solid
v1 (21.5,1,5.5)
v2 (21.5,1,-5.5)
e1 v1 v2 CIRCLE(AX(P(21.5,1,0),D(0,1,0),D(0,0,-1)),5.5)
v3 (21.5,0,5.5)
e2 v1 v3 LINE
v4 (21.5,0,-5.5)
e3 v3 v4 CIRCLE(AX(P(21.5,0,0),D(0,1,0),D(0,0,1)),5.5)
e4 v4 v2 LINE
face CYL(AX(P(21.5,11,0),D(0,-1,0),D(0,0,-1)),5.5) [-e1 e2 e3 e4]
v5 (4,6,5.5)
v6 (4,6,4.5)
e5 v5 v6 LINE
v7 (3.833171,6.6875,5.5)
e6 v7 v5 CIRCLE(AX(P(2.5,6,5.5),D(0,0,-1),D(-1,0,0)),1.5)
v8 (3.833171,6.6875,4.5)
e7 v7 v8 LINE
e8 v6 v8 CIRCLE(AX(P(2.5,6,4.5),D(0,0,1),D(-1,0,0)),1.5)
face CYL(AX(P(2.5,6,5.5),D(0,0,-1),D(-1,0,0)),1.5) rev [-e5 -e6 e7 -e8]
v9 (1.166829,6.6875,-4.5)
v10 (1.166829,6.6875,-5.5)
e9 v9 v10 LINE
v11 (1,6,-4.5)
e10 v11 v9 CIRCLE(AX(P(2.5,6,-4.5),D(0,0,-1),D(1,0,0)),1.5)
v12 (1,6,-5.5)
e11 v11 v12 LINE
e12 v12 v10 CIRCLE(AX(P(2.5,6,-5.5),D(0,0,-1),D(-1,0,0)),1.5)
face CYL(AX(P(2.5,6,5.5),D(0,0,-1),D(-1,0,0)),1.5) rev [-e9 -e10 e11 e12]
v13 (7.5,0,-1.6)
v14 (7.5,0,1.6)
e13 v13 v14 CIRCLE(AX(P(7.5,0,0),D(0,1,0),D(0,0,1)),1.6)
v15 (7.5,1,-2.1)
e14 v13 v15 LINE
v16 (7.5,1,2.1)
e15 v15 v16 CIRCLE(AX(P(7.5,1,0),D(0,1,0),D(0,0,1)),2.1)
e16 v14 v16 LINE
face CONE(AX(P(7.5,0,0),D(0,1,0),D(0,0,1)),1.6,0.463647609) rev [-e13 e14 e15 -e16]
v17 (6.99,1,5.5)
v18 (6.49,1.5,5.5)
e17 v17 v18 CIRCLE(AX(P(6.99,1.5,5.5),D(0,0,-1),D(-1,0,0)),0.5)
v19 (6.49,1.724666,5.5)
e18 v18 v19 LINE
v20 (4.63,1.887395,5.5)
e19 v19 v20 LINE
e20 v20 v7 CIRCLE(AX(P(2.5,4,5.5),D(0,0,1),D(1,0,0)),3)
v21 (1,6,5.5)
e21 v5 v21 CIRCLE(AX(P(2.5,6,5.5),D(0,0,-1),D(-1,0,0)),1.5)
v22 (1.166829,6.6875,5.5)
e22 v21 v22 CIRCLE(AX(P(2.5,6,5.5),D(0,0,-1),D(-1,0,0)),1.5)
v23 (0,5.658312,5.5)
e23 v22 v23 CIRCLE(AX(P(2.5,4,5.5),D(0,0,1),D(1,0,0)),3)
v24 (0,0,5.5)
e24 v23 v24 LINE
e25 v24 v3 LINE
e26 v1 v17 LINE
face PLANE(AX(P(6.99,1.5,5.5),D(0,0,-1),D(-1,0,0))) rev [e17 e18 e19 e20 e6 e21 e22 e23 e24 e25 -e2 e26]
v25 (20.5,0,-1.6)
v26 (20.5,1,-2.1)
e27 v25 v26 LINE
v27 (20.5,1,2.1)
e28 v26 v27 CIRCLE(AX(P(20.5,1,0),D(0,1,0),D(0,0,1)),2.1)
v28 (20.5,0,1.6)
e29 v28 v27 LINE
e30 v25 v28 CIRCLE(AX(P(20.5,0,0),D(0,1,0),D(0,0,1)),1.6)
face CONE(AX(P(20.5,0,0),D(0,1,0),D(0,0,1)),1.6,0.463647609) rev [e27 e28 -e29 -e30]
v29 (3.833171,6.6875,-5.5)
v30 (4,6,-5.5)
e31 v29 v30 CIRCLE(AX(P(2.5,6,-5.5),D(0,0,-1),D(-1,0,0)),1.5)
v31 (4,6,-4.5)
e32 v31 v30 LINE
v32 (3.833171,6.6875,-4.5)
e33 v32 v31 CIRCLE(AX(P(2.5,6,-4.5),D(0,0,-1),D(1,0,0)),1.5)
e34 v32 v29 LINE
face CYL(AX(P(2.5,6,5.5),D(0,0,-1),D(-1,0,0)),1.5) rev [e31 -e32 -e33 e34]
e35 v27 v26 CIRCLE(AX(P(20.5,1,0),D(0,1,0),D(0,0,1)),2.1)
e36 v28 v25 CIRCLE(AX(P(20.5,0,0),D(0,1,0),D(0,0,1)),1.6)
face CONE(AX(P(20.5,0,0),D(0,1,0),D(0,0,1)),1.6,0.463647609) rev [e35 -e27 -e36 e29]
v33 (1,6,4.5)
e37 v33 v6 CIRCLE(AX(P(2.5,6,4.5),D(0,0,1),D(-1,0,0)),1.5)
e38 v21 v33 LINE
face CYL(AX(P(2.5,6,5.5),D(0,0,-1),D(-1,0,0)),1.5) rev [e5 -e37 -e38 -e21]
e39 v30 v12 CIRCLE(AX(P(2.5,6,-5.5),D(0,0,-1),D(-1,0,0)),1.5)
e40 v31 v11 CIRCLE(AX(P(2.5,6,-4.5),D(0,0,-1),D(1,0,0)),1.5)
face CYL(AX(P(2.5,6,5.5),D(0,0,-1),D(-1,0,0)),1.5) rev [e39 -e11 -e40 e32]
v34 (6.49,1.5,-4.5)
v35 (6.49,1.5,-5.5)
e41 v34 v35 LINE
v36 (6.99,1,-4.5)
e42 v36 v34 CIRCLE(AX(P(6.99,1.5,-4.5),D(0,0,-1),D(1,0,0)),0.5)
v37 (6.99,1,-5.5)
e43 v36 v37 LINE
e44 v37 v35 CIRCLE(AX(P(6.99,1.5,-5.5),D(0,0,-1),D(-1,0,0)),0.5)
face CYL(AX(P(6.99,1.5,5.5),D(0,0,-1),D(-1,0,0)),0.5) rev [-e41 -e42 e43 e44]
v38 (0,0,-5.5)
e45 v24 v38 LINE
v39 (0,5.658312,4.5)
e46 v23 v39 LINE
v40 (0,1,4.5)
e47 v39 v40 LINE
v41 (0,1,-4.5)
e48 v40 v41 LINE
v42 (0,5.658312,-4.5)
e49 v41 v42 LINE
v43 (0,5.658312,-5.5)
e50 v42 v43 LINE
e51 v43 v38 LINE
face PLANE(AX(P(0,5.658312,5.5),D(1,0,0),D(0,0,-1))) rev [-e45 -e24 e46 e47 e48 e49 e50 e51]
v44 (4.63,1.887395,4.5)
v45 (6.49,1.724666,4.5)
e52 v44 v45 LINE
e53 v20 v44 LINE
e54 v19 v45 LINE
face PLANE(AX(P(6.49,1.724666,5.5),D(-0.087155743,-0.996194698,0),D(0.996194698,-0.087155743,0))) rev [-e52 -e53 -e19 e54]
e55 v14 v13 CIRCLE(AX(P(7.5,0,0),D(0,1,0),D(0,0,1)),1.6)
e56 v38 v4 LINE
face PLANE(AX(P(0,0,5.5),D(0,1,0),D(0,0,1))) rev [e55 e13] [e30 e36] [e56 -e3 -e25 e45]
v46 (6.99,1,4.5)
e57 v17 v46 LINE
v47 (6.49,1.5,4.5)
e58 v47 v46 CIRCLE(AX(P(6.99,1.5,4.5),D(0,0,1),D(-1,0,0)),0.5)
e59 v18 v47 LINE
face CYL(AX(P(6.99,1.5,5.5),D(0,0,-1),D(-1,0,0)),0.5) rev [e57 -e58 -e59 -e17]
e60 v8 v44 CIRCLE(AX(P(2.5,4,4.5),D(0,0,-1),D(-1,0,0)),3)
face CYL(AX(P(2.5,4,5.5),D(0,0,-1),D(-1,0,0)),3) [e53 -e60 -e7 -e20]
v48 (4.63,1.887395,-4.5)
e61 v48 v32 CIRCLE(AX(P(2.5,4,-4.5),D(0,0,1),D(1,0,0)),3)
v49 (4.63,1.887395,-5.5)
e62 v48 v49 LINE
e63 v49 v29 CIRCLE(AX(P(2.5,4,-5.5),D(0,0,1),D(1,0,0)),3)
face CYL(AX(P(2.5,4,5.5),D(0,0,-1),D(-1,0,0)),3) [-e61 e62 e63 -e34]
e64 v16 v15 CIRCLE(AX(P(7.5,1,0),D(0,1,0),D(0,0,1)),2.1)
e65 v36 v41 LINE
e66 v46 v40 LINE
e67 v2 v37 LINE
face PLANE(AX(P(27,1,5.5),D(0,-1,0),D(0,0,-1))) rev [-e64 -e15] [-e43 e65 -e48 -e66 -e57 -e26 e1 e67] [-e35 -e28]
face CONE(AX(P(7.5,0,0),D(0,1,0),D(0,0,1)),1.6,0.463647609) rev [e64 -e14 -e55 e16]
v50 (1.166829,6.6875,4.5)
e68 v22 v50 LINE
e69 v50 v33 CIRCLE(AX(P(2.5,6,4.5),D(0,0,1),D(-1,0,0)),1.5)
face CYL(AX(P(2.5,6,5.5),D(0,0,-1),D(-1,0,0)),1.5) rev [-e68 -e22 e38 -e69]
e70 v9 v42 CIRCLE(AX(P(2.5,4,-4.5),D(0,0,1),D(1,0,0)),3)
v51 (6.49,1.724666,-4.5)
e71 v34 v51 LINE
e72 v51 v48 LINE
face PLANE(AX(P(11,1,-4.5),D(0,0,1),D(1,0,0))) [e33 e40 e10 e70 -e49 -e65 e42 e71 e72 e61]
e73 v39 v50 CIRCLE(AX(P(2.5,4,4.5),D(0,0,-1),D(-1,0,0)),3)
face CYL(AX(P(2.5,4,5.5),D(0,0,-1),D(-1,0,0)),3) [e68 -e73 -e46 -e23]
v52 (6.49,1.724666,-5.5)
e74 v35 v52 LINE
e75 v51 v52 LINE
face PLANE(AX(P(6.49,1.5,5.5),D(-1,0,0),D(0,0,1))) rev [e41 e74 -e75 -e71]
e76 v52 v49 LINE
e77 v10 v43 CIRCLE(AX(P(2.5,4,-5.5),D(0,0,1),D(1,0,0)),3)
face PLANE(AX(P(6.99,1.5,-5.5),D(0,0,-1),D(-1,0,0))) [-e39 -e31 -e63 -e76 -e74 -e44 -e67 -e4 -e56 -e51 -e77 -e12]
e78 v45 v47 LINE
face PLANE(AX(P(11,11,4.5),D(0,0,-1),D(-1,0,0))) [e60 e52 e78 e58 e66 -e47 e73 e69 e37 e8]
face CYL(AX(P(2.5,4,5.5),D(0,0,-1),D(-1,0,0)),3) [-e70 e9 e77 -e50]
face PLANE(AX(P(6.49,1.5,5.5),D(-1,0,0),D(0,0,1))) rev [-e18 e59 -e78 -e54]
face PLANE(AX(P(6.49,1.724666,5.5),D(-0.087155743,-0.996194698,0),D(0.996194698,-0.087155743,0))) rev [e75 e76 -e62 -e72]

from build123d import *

# Parameters (mm, degrees)
BOSS_EXTRUDE1_DEPTH      = 5.5
BOSS_EXTRUDE1_DEPTH_BACK = 5.5
SKETCH2_W                = 108
SKETCH2_H                = 22
CUT_EXTRUDE1_DEPTH       = 11
SKETCH4_W                = 9
SKETCH4_H                = 10
CUT_EXTRUDE2_DEPTH       = 11


with BuildPart() as part:
    # Sketch1 → Boss-Extrude1 (new, two sides: drawn at the far end of the back side and taken through both)
    with BuildSketch(Plane.XY.offset(-BOSS_EXTRUDE1_DEPTH_BACK)):
        with BuildLine():
            Line((0, 0), (27, 0))
            Line((27, 0), (27, 1))
            Line((27, 1), (6.99, 1))
            ThreePointArc((6.99, 1), (6.636446609, 1.146446609), (6.49, 1.5))
            Line((6.49, 1.5), (6.49, 1.724666059))
            Line((6.49, 1.724666059), (4.63, 1.887394973))
            ThreePointArc((4.63, 1.887394973), (5.459499899, 4.491284383), (3.833170563, 6.6875))
            ThreePointArc((3.833170563, 6.6875), (2.5, 4.5), (1.166829437, 6.6875))
            ThreePointArc((1.166829437, 6.6875), (0.515533844, 6.249865346), (0, 5.658312395))
            Line((0, 5.658312395), (0, 0))
        make_face()
    extrude(amount=BOSS_EXTRUDE1_DEPTH + BOSS_EXTRUDE1_DEPTH_BACK)

    # Sketch2 → Cut-Extrude1 (cut)
    with BuildSketch(Plane(origin=(0, 0, 0), x_dir=(1, 0, 0), z_dir=(0, 1, 0))):
        Rectangle(SKETCH2_W, SKETCH2_H)
        with BuildLine():
            Line((0, 5.5), (0, -5.5))
            Line((0, -5.5), (21.5, -5.5))
            ThreePointArc((21.5, -5.5), (27, 0), (21.5, 5.5))
            Line((21.5, 5.5), (0, 5.5))
        make_face(mode=Mode.SUBTRACT)
    extrude(amount=CUT_EXTRUDE1_DEPTH, mode=Mode.SUBTRACT)

    # Sketch4 → Cut-Extrude2 (cut)
    with BuildSketch(Plane(origin=(0, 0, 0), x_dir=(0, 0, -1), z_dir=(1, 0, 0))):
        with Locations((0, 6)):
            Rectangle(SKETCH4_W, SKETCH4_H)
    extrude(amount=CUT_EXTRUDE2_DEPTH, mode=Mode.SUBTRACT)

    # Sketch3 → Cut-Revolve1 (revolve, cut)
    with BuildSketch(Plane.XY, mode=Mode.PRIVATE) as cut_revolve1_sk:
        Polygon((7.5, 1), (9.6, 1), (9.1, 0), (7.5, 0), align=None)
    revolve(cut_revolve1_sk.sketch.rotate(Axis((7.5, 0, 0), (0, 1, 0)), 270), axis=Axis((7.5, 0, 0), (0, 1, 0)), mode=Mode.SUBTRACT)

    # Sketch5 → Cut-Revolve2 (revolve, cut)
    with BuildSketch(Plane.XY, mode=Mode.PRIVATE) as cut_revolve2_sk:
        Polygon((20.5, 1), (22.6, 1), (22.1, 0), (20.5, 0), align=None)
    revolve(cut_revolve2_sk.sketch.rotate(Axis((20.5, 0, 0), (0, 1, 0)), 270), axis=Axis((20.5, 0, 0), (0, 1, 0)), mode=Mode.SUBTRACT)


solid = part.part
